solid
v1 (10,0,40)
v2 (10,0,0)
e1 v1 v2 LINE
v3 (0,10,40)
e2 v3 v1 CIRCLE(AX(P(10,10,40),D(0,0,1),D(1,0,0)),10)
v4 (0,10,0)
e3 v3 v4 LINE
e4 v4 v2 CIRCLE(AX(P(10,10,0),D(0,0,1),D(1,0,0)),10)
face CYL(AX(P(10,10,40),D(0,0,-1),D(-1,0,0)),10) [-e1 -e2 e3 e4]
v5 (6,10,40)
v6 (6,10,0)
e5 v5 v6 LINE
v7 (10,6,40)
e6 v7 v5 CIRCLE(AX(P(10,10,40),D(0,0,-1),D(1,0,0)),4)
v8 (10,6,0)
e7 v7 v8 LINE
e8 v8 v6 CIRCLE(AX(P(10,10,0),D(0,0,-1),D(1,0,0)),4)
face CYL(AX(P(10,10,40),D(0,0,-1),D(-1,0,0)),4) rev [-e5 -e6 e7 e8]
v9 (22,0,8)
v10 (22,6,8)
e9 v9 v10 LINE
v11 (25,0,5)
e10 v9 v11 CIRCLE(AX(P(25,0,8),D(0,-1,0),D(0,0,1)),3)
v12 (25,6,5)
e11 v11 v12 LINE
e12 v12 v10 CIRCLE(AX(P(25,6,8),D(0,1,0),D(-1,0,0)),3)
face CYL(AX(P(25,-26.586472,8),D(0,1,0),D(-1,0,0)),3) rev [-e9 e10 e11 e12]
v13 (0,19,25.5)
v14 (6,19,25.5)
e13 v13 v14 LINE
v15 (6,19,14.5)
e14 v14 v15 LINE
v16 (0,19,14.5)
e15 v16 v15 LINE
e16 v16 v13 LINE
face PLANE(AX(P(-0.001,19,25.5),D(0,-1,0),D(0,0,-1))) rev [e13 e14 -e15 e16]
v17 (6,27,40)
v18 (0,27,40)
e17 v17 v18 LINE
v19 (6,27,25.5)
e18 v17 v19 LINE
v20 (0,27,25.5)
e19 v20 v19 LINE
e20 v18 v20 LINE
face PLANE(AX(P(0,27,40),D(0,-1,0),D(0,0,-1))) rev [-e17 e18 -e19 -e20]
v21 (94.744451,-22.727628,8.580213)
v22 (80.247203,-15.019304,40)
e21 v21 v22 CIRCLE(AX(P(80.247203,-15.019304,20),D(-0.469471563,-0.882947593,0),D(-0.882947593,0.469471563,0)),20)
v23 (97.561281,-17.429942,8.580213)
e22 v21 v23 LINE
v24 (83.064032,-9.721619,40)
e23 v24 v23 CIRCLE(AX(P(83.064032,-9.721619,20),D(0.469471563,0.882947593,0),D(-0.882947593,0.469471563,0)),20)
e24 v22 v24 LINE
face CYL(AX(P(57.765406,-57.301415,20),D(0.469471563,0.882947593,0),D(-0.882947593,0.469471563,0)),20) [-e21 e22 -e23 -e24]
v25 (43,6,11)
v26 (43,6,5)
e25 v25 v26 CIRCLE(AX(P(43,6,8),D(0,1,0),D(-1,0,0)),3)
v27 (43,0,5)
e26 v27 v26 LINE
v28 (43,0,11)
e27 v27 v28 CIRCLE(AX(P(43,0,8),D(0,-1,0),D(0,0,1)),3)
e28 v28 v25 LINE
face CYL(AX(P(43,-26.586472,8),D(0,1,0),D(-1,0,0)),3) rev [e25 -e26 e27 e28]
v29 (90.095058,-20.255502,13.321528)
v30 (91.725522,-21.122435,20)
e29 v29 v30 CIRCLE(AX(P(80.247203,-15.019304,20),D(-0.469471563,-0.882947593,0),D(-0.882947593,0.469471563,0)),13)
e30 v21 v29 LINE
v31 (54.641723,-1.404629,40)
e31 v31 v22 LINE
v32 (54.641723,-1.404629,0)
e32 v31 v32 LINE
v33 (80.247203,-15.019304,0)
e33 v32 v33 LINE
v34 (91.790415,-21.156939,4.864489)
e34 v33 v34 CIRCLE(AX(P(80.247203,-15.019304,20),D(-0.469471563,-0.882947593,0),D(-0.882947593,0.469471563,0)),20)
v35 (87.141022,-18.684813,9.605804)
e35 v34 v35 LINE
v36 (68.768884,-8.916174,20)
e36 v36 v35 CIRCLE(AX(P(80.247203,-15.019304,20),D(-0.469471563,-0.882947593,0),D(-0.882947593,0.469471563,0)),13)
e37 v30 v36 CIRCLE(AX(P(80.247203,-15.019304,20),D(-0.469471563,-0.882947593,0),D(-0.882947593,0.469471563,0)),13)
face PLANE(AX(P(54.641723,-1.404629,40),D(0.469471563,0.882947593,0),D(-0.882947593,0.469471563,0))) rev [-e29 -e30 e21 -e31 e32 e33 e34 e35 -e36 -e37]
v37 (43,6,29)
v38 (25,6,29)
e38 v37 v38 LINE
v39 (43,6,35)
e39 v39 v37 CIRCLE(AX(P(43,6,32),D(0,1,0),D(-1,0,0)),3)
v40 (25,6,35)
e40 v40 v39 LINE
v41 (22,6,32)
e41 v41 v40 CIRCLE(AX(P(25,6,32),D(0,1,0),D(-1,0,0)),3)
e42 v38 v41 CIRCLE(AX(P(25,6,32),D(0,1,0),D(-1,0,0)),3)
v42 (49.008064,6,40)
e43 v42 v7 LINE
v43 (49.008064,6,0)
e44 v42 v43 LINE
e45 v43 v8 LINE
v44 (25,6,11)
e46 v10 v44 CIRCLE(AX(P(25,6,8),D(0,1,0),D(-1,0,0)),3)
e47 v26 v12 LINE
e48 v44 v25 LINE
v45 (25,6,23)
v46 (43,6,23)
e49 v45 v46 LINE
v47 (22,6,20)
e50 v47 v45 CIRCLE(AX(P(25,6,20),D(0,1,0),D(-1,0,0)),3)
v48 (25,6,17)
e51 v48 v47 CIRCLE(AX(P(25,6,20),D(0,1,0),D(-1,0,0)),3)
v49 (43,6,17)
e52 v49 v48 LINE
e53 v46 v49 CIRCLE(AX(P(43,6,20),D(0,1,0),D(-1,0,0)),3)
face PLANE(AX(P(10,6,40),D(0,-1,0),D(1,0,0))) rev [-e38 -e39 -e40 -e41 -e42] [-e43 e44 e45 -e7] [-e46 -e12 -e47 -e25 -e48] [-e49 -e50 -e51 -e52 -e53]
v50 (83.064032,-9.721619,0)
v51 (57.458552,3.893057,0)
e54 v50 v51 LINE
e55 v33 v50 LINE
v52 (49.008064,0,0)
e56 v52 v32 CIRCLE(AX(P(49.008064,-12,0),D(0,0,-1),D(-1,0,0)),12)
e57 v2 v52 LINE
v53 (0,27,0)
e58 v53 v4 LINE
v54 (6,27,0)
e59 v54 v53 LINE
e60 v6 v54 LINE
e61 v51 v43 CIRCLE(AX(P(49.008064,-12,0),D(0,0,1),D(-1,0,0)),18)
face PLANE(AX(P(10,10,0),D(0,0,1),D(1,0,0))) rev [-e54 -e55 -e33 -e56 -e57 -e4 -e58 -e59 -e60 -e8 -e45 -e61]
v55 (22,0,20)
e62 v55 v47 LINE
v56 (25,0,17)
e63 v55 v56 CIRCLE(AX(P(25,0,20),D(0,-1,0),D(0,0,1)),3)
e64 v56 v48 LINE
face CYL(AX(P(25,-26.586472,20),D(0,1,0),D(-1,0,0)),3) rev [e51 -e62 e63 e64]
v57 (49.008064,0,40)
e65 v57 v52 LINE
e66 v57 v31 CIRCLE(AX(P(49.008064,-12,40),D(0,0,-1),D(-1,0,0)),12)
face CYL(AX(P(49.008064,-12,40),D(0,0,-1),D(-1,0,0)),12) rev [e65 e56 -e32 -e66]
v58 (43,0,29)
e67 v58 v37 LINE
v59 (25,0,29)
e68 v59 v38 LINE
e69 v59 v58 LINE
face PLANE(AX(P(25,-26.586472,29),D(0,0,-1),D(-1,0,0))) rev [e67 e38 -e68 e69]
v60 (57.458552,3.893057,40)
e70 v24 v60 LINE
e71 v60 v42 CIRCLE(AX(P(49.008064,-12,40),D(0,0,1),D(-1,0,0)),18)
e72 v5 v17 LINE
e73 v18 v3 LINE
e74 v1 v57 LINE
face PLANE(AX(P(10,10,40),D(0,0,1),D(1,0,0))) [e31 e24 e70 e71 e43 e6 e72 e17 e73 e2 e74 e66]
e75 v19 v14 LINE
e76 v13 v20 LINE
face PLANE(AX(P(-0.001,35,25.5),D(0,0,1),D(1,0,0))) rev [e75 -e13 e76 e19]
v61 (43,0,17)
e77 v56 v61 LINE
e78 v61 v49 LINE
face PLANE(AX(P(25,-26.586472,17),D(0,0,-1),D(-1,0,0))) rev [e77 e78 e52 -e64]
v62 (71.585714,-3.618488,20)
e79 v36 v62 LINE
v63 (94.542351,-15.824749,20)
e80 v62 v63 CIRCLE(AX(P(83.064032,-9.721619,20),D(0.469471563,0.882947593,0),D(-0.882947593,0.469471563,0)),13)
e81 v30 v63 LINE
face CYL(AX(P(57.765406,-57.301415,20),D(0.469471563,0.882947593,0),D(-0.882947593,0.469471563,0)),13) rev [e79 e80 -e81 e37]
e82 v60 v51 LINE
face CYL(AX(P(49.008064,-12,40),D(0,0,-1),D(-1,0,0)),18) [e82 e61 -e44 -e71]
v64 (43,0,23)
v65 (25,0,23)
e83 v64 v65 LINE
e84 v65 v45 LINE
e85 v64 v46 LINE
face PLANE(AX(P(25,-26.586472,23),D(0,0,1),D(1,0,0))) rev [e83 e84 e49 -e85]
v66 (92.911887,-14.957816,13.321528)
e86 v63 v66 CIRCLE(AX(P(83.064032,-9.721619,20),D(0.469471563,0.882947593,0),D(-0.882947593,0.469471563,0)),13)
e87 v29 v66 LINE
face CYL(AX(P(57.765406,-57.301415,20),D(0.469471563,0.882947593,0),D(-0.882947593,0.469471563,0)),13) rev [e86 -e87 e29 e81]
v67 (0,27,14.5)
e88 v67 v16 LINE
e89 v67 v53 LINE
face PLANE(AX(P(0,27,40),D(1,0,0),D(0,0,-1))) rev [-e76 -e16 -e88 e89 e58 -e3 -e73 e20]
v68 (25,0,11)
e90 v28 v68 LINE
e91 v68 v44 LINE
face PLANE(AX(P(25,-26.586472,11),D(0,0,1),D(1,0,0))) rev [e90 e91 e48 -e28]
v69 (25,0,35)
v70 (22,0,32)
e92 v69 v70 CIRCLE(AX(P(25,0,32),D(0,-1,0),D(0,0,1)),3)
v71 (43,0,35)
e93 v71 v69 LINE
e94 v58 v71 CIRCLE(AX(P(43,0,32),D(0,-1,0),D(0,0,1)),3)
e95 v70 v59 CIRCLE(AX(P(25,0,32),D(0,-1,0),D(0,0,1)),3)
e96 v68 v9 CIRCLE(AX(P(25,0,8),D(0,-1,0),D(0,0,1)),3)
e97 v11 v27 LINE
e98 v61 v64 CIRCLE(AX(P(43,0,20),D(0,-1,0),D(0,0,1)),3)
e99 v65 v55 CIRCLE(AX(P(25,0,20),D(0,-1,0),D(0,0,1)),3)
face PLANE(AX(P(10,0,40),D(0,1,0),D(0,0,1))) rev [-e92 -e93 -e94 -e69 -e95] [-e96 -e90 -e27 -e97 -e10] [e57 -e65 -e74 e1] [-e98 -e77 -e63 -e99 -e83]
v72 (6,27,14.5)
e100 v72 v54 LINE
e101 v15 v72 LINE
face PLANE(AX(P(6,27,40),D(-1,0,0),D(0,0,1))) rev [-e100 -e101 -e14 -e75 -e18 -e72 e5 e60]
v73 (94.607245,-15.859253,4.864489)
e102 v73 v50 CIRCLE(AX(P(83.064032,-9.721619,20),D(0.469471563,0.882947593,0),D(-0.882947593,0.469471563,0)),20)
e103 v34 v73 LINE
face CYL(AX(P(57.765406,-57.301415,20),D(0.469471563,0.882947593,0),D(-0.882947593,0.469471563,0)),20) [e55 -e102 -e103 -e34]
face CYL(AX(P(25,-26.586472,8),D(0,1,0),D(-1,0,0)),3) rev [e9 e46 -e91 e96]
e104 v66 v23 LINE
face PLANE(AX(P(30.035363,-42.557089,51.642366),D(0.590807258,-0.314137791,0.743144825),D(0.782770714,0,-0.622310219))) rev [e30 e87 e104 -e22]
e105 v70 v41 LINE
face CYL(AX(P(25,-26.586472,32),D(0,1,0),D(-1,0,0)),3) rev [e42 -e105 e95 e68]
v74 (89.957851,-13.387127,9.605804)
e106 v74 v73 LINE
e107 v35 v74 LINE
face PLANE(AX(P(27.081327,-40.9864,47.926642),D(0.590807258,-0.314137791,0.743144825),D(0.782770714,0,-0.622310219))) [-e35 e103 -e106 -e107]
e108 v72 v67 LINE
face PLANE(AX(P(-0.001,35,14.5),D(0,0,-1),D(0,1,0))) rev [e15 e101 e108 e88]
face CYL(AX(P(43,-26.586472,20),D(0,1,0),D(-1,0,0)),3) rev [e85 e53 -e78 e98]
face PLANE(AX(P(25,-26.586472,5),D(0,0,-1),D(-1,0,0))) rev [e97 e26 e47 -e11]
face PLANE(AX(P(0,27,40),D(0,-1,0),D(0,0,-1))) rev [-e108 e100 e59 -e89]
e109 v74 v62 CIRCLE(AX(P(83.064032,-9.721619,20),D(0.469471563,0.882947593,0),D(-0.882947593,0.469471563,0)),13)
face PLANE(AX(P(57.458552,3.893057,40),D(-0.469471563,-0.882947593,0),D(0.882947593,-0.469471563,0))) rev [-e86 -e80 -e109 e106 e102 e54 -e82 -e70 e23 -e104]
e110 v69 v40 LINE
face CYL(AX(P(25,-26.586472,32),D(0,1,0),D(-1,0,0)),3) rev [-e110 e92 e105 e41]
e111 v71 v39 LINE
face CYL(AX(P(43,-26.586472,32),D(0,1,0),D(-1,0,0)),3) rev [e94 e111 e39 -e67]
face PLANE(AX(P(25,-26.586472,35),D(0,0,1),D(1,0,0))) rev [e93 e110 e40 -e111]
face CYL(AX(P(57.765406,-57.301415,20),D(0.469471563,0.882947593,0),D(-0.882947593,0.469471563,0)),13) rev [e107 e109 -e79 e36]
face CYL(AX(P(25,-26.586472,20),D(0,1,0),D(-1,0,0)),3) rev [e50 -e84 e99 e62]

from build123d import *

# Parameters (mm, degrees)
BENT_STRAP_BODY_DEPTH      = 40
SLOTS_3X6_WIDE_REACH       = 118.826
SPLIT_CLAMP_RING_CUT_REACH = 114.485
END_TAB_NOTCH_11X8_REACH   = 108.308
END_TAB_NOTCH_SKETCH_W     = 11
END_TAB_NOTCH_SKETCH_H     = 16


with BuildPart() as part:
    # Strap Profile Sketch → Bent Strap Body (new body)
    with BuildSketch(Plane.XY):
        with BuildLine():
            Line((0, 27), (0, 10))
            ThreePointArc((0, 10), (2.928932188, 2.928932188), (10, 0))
            Line((10, 0), (49.008063966, 0))
            ThreePointArc((49.008063966, 0), (51.911126713, -0.356451285), (54.641722719, -1.404628886))
            Line((54.641722719, -1.404628886), (102, -26.585471583))
            Line((102, -26.585471583), (104.816829377, -21.287786026))
            Line((104.816829377, -21.287786026), (57.458552096, 3.893056671))
            ThreePointArc((57.458552096, 3.893056671), (53.362658087, 5.465323073), (49.008063966, 6))
            Line((49.008063966, 6), (10, 6))
            ThreePointArc((10, 6), (7.171572875, 7.171572875), (6, 10))
            Line((6, 10), (6, 27))
            Line((6, 27), (0, 27))
        make_face()
    extrude(amount=BENT_STRAP_BODY_DEPTH)

    # Slots Sketch → Slots 3x6 Wide (cut, up to next)
    with BuildSketch(Plane(origin=(0, 6, 0), x_dir=(1, 0, 0), z_dir=(0, 1, 0)), mode=Mode.PRIVATE) as slots_3x6_wide_sk1:
        with BuildLine():
            Line((25, -17), (43, -17))
            ThreePointArc((43, -17), (46, -20), (43, -23))
            Line((43, -23), (25, -23))
            ThreePointArc((25, -23), (22, -20), (25, -17))
        make_face()
    slots_3x6_wide_tool1 = extrude(slots_3x6_wide_sk1.sketch, amount=-SLOTS_3X6_WIDE_REACH, mode=Mode.PRIVATE) & part.part
    # Slots Sketch → Slots 3x6 Wide (cut, up to next)
    with BuildSketch(Plane(origin=(0, 6, 0), x_dir=(1, 0, 0), z_dir=(0, 1, 0)), mode=Mode.PRIVATE) as slots_3x6_wide_sk2:
        with BuildLine():
            Line((25, -5), (43, -5))
            ThreePointArc((43, -5), (46, -8), (43, -11))
            Line((43, -11), (25, -11))
            ThreePointArc((25, -11), (22, -8), (25, -5))
        make_face()
    slots_3x6_wide_tool2 = extrude(slots_3x6_wide_sk2.sketch, amount=-SLOTS_3X6_WIDE_REACH, mode=Mode.PRIVATE) & part.part
    # Slots Sketch → Slots 3x6 Wide (cut, up to next)
    with BuildSketch(Plane(origin=(0, 6, 0), x_dir=(1, 0, 0), z_dir=(0, 1, 0)), mode=Mode.PRIVATE) as slots_3x6_wide_sk3:
        with BuildLine():
            Line((25, -29), (43, -29))
            ThreePointArc((43, -29), (46, -32), (43, -35))
            Line((43, -35), (25, -35))
            ThreePointArc((25, -35), (22, -32), (25, -29))
        make_face()
    slots_3x6_wide_tool3 = extrude(slots_3x6_wide_sk3.sketch, amount=-SLOTS_3X6_WIDE_REACH, mode=Mode.PRIVATE) & part.part
    add(slots_3x6_wide_tool1.solids().sort_by_distance((34, 6, 20))[0], mode=Mode.SUBTRACT)
    add(slots_3x6_wide_tool2.solids().sort_by_distance((34, 6, 8))[0], mode=Mode.SUBTRACT)
    add(slots_3x6_wide_tool3.solids().sort_by_distance((34, 6, 32))[0], mode=Mode.SUBTRACT)

    # Split Clamp Ring Sketch → Split Clamp Ring Cut (cut, up to next)
    with BuildSketch(Plane(origin=(14.277813886, 26.852662444, 0), x_dir=(0.8829475928589264, -0.46947156278589186, 0), z_dir=(0.46947156278589186, 0.8829475928589264, 0)), mode=Mode.PRIVATE) as split_clamp_ring_cut_sk1:
        with BuildLine():
            Line((90.978707319, -4.864489093), (85.712943597, -9.605804045))
            ThreePointArc((85.712943597, -9.605804045), (68.244328132, -28.698697883), (89.058596629, -13.321528173))
            Line((89.058596629, -13.321528173), (94.324360351, -8.580213221))
            ThreePointArc((94.324360351, -8.580213221), (95.630838293, -29.262944036), (77.905210863, -40))
            Line((77.905210863, -40), (102.541777363, -40))
            Line((102.541777363, -40), (102.541777363, 0))
            Line((102.541777363, 0), (77.905210863, 0))
            ThreePointArc((77.905210863, 0), (84.879799807, -1.255531241), (90.978707319, -4.864489093))
        make_face()
    split_clamp_ring_cut_tool1 = extrude(split_clamp_ring_cut_sk1.sketch, amount=-SPLIT_CLAMP_RING_CUT_REACH, mode=Mode.PRIVATE) & part.part
    add(split_clamp_ring_cut_tool1.solids().sort_by_distance((89.983505, -13.400768, 19.581438))[0], mode=Mode.SUBTRACT)

    # End Tab Notch Sketch → End Tab Notch 11x8 (cut, up to next)
    with BuildSketch(Plane(origin=(6, 0, 0), x_dir=(0, 0, -1), z_dir=(1, 0, 0)), mode=Mode.PRIVATE) as end_tab_notch_11x8_sk1:
        with Locations((-20, 27)):
            Rectangle(END_TAB_NOTCH_SKETCH_W, END_TAB_NOTCH_SKETCH_H)
    end_tab_notch_11x8_tool1 = extrude(end_tab_notch_11x8_sk1.sketch, amount=-END_TAB_NOTCH_11X8_REACH, mode=Mode.PRIVATE) & part.part
    add(end_tab_notch_11x8_tool1.solids().sort_by_distance((6, 27, 20))[0], mode=Mode.SUBTRACT)


solid = part.part
